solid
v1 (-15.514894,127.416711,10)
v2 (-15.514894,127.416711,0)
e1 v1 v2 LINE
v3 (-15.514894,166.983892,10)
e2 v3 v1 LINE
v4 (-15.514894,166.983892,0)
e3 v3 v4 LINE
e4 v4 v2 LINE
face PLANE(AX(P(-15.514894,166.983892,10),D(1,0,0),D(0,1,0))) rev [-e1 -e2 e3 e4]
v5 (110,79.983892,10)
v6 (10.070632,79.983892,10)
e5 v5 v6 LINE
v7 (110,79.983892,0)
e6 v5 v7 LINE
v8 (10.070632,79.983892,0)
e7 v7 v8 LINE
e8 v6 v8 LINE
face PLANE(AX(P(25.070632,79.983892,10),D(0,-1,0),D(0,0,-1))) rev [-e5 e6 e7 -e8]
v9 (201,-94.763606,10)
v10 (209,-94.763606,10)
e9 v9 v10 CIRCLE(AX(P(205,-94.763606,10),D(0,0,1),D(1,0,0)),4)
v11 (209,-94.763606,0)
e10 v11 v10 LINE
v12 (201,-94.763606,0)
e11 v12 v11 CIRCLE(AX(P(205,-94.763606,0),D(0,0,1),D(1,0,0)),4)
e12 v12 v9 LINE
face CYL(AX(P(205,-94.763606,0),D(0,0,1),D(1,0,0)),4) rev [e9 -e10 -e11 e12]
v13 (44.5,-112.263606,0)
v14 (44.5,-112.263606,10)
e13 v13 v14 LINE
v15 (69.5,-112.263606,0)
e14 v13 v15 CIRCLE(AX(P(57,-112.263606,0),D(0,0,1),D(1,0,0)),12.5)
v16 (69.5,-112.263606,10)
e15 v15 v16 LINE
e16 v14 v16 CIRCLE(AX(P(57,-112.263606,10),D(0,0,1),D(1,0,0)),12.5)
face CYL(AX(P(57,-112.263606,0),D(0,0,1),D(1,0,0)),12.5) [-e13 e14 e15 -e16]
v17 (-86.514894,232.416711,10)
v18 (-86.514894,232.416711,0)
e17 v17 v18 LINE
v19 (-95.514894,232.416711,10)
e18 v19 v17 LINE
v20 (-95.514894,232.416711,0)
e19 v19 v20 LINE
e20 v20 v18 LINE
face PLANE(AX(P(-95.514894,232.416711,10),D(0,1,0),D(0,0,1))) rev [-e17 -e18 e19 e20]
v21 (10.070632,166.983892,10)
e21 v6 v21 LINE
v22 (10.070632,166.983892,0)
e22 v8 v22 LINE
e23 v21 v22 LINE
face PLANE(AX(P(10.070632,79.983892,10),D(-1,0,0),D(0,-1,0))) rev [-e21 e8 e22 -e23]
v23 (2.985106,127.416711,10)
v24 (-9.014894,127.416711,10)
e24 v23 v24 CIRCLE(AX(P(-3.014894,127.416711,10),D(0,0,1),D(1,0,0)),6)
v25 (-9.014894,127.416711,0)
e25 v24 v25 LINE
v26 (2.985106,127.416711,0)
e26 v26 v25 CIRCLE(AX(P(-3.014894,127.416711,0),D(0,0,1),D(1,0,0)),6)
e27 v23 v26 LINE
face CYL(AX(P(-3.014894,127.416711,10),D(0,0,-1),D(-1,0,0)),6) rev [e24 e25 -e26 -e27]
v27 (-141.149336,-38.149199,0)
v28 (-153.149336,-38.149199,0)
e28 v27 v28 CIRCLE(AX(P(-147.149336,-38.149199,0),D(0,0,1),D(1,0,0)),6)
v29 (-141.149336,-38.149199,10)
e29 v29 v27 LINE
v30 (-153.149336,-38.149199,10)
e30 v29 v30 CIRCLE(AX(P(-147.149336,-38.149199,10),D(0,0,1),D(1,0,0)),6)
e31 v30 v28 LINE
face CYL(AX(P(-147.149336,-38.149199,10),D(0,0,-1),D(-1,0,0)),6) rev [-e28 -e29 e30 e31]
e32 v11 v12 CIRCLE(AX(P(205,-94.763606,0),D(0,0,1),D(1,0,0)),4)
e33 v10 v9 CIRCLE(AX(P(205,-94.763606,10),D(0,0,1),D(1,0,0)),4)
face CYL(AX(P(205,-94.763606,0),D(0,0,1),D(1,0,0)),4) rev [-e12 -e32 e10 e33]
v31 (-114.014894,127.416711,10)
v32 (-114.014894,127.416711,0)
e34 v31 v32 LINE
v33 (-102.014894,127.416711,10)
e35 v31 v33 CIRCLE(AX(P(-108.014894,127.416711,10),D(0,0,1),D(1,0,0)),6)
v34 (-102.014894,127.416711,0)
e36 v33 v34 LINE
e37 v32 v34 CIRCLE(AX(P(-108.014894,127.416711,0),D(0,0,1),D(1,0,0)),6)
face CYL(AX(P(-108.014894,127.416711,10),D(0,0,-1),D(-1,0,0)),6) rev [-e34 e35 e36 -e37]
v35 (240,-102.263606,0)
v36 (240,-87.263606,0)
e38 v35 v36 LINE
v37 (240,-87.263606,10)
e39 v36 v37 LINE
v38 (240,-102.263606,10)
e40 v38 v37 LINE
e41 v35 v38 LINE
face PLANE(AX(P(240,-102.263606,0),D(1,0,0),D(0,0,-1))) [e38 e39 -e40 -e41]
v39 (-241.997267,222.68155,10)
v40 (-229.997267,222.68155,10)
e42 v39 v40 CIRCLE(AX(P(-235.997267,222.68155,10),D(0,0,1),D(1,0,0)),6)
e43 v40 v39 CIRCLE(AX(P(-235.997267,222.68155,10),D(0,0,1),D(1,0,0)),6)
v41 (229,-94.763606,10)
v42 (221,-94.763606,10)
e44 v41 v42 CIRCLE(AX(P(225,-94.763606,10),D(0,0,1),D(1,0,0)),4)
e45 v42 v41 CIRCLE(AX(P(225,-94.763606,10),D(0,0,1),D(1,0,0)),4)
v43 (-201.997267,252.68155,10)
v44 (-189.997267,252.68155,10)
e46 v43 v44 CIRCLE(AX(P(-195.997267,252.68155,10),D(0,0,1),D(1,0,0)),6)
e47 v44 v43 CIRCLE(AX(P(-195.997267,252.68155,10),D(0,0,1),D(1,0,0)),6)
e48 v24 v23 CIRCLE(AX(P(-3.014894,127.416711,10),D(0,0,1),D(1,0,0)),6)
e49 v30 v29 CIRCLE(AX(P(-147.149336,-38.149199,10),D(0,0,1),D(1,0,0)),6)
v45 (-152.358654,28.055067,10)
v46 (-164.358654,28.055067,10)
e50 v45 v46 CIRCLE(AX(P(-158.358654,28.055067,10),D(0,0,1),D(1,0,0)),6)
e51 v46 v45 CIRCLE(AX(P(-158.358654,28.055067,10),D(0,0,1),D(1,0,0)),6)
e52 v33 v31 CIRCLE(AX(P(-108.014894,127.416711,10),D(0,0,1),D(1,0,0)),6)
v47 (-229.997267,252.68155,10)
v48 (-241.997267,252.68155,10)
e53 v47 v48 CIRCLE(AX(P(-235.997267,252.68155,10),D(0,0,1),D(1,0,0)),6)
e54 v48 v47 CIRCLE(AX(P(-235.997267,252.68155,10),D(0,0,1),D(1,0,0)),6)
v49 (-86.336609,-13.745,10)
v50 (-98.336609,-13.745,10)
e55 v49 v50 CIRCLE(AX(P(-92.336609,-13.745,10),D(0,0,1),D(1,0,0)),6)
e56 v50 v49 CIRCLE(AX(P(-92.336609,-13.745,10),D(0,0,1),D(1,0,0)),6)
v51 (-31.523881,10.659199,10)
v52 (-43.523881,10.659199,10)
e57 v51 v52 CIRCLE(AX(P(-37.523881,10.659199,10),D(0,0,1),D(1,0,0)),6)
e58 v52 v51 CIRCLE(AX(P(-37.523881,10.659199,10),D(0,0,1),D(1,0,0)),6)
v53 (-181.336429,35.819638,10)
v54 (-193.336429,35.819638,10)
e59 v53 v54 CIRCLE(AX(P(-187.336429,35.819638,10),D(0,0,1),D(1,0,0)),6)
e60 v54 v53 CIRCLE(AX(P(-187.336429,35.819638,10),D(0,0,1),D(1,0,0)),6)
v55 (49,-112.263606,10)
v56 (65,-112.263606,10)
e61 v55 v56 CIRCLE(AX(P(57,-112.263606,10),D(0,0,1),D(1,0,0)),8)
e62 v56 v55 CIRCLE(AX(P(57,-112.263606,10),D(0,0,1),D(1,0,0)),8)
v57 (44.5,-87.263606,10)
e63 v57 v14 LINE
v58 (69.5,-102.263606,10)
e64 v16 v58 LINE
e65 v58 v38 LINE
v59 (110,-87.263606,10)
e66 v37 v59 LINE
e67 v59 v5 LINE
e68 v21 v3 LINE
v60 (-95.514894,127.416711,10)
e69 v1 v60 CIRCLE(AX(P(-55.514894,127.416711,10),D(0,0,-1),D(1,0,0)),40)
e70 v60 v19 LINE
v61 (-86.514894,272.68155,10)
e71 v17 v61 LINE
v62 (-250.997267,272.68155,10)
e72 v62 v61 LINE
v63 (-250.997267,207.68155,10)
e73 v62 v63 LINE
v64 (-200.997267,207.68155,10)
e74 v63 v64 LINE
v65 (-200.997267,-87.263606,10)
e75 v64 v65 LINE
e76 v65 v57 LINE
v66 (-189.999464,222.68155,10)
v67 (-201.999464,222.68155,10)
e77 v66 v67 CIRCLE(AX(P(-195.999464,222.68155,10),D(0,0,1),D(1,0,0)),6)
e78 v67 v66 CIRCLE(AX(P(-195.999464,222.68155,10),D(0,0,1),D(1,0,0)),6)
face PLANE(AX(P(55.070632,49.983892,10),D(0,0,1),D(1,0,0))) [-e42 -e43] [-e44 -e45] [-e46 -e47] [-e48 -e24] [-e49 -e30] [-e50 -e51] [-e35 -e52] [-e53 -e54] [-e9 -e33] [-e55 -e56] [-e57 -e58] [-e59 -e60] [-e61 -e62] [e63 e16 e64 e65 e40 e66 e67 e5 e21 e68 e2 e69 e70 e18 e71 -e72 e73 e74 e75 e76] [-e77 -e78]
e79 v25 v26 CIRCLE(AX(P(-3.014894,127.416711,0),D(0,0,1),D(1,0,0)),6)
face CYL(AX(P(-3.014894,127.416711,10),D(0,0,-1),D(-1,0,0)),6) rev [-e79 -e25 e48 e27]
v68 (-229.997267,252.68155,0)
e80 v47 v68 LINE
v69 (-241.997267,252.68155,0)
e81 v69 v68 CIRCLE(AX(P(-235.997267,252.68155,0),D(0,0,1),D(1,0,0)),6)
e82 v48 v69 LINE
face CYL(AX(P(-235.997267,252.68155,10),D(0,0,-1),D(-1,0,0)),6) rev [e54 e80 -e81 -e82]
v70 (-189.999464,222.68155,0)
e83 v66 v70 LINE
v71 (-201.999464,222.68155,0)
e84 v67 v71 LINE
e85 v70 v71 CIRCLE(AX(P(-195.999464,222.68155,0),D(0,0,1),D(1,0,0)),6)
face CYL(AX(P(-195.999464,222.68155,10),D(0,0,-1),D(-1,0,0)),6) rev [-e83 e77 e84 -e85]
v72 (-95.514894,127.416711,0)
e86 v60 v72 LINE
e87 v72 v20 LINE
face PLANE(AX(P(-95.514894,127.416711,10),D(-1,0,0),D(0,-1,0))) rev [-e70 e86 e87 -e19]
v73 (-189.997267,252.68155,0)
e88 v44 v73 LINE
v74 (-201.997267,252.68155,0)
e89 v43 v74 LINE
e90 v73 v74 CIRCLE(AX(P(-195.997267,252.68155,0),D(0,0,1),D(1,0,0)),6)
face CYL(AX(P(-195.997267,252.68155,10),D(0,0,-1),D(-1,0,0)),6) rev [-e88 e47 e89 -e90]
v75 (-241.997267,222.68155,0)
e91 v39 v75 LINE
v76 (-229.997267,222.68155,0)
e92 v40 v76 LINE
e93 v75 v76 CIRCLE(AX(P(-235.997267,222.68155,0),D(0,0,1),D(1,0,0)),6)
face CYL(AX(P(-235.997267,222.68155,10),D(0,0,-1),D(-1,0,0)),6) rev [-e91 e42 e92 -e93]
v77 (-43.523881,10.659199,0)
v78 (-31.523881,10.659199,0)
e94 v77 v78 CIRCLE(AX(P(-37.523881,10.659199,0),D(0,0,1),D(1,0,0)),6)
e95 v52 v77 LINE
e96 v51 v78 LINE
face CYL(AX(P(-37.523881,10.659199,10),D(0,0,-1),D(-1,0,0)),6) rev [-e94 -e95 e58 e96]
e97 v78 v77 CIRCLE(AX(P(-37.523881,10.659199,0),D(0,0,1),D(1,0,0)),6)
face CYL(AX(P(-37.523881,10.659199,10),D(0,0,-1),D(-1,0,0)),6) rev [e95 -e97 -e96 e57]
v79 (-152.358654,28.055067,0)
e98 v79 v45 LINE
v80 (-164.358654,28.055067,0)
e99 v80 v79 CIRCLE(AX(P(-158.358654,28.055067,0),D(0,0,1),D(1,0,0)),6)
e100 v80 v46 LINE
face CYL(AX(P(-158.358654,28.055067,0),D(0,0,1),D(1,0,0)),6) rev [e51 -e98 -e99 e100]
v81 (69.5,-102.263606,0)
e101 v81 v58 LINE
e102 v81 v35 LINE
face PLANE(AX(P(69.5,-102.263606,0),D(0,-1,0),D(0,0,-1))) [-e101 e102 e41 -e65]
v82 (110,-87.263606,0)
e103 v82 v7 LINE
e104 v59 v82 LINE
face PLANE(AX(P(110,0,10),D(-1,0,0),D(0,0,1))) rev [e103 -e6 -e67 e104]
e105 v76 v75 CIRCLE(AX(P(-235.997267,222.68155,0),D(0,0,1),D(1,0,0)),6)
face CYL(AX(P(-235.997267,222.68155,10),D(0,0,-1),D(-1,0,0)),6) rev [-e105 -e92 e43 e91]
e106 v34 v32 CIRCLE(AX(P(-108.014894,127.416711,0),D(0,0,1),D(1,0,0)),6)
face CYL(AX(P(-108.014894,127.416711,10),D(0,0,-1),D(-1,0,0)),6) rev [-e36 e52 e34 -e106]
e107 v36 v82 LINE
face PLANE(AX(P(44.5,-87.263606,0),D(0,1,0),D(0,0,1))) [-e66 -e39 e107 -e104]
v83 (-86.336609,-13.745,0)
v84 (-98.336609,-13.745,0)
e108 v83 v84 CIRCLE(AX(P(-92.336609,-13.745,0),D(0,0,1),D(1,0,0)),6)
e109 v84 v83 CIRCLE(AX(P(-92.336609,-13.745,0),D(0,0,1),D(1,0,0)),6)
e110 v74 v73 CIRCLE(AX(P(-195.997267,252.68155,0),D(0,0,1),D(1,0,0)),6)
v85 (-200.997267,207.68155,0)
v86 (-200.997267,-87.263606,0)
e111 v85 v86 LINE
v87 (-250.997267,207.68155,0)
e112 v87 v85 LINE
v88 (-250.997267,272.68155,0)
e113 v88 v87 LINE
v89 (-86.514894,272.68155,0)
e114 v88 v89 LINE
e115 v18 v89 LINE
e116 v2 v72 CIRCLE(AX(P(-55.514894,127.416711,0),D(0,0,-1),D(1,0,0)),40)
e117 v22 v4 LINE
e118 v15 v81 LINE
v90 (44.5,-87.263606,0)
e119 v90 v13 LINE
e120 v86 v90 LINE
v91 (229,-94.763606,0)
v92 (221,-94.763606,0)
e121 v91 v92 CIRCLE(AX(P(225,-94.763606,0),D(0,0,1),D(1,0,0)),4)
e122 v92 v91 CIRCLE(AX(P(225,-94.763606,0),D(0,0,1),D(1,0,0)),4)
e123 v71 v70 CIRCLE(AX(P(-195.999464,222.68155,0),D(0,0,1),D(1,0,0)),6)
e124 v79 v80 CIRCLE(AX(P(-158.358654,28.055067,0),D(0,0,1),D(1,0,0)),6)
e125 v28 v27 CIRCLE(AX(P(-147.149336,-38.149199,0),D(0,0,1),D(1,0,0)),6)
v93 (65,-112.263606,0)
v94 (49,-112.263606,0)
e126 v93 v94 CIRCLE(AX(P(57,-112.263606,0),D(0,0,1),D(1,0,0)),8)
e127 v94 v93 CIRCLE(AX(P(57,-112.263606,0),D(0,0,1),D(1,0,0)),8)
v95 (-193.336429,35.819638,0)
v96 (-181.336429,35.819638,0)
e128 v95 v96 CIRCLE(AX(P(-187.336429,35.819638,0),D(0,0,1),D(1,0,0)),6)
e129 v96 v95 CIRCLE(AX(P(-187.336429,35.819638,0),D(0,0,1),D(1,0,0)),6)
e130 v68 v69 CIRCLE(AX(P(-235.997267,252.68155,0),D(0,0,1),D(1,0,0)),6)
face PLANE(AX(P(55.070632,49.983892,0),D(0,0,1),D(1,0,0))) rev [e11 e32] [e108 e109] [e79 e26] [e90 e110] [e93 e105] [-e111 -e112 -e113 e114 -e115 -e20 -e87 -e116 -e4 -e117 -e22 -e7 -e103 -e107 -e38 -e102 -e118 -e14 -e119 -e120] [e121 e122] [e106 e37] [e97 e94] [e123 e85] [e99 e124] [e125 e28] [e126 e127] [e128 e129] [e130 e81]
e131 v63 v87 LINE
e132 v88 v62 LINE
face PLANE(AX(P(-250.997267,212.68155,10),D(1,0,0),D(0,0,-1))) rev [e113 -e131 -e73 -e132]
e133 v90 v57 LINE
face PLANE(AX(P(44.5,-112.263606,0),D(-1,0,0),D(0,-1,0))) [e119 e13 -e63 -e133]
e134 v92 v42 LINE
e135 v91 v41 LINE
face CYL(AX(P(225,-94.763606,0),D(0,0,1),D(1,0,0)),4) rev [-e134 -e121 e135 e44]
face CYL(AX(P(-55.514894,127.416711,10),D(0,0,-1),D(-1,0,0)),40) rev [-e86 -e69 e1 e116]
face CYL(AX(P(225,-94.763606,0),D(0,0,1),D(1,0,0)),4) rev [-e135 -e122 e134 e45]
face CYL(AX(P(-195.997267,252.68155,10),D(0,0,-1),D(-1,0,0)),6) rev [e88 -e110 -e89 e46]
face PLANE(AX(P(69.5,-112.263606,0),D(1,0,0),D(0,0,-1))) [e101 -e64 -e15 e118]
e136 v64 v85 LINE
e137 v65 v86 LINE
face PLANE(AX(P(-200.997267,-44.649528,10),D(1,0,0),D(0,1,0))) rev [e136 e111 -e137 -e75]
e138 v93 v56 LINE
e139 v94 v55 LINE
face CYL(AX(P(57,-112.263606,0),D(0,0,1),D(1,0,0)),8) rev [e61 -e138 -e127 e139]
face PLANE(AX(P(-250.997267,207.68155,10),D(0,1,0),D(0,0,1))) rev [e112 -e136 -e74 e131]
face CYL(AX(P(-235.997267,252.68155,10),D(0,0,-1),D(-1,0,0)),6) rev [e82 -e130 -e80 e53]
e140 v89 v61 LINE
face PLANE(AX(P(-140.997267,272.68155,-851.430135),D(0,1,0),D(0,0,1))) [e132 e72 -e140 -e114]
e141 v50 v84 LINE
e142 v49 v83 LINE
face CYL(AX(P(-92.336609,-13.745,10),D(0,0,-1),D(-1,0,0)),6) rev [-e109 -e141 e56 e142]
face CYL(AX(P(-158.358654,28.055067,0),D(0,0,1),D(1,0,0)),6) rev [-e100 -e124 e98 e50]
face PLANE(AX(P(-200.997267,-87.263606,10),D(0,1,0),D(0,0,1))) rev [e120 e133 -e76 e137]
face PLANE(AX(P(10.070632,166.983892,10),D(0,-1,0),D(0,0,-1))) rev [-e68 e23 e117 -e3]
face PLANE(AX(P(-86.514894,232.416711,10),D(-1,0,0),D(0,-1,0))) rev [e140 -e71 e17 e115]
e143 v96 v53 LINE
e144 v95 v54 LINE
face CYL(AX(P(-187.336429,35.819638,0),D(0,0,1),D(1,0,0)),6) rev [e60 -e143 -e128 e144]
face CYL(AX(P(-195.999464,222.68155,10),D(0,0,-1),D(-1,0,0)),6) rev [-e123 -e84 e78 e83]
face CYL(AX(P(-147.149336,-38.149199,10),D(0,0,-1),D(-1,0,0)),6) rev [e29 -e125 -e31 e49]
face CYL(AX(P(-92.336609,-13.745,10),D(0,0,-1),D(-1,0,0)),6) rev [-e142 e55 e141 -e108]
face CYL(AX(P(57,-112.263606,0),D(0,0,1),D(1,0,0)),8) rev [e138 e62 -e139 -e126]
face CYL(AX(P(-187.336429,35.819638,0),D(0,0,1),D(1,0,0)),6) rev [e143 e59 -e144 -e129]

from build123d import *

# Parameters (mm, degrees)
SKETCH_1_R               = 5
SKETCH_1_R_2             = 6
EXTRUDE_1_DEPTH          = 10
SKETCH_2_R               = 6
CUT_EXTRUDE_1_DEPTH      = 10
SKETCH_3_R               = 8
SKETCH_3_R_2             = 4
EXTRUDE_2_DEPTH          = 10
CUT_EXTRUDE_3_DEPTH      = 417.865256367
CUT_EXTRUDE_3_DEPTH_BACK = 10
SKETCH_4_R               = 5
SKETCH_5_R               = 5
EXTRUDE_3_DEPTH          = 10
SKETCH_6_R               = 5
EXTRUDE_4_DEPTH          = 10
EXTRUDE_5_DEPTH          = 10


with BuildPart() as part:
    # 草图1 → 凸台-拉伸1 (new body)
    with BuildSketch(Plane.XY):
        with BuildLine():
            Line((-200.997267146, -87.263605576), (110, -87.263605576))
            Line((110, -87.263605576), (110, 0))
            Line((110, 0), (110, 79.983892276))
            Line((110, 79.983892276), (85.070632456, 79.983892276))
            Line((85.070632456, 79.983892276), (85.070632456, 49.983892276))
            ThreePointArc((85.070632456, 49.983892276), (55.070632456, 19.983892276), (25.070632456, 49.983892276))
            Line((25.070632456, 49.983892276), (25.070632456, 79.983892276))
            Line((25.070632456, 79.983892276), (10.070632456, 79.983892276))
            Line((10.070632456, 79.983892276), (10.070632456, 166.983892276))
            Line((10.070632456, 166.983892276), (-15.514893523, 166.983892276))
            Line((-15.514893523, 166.983892276), (-15.514893523, 127.416711183))
            ThreePointArc((-15.514893523, 127.416711183), (-55.514893523, 87.416711183), (-95.514893523, 127.416711183))
            Line((-95.514893523, 127.416711183), (-95.514893523, 232.416711183))
            Line((-95.514893523, 232.416711183), (-86.514893523, 232.416711183))
            Line((-86.514893523, 232.416711183), (-86.514893523, 332.416711183))
            Line((-86.514893523, 332.416711183), (-110.997267146, 332.416711183))
            Line((-110.997267146, 332.416711183), (-110.997267146, 302.681550212))
            ThreePointArc((-110.997267146, 302.681550212), (-140.997267146, 272.681550212), (-170.997267146, 302.681550212))
            Line((-170.997267146, 302.681550212), (-170.997267146, 332.681550212))
            Line((-170.997267146, 332.681550212), (-200.997267146, 332.681550212))
            Line((-200.997267146, 332.681550212), (-250.997267146, 332.681550212))
            Line((-250.997267146, 332.681550212), (-250.997267146, 212.681550212))
            Line((-250.997267146, 212.681550212), (-250.997267146, 207.681550212))
            Line((-250.997267146, 207.681550212), (-200.997267146, 207.681550212))
            Line((-200.997267146, 207.681550212), (-200.997267146, 182.681550212))
            Line((-200.997267146, 182.681550212), (-200.997267146, -44.649528276))
            Line((-200.997267146, -44.649528276), (-200.997267146, -87.263605576))
        make_face()
        with Locations((96.070632456, 49.983892276)):
            Circle(SKETCH_1_R, mode=Mode.SUBTRACT)
        with Locations((14.070632456, 49.983892276)):
            Circle(SKETCH_1_R, mode=Mode.SUBTRACT)
        with Locations((-3.014893523, 127.416711183)):
            Circle(SKETCH_1_R_2, mode=Mode.SUBTRACT)
        with Locations((-108.014893523, 127.416711183)):
            Circle(SKETCH_1_R_2, mode=Mode.SUBTRACT)
        with Locations((-99.997267146, 302.681550212)):
            Circle(SKETCH_1_R, mode=Mode.SUBTRACT)
        with Locations((-181.997266842, 302.67655009)):
            Circle(SKETCH_1_R, mode=Mode.SUBTRACT)
        with Locations((-37.523881476, 10.659198545)):
            Circle(SKETCH_1_R_2, mode=Mode.SUBTRACT)
        with Locations((-92.336608934, -13.745000039)):
            Circle(SKETCH_1_R_2, mode=Mode.SUBTRACT)
        with Locations((-147.149336393, -38.149198624)):
            Circle(SKETCH_1_R_2, mode=Mode.SUBTRACT)
        with Locations((-235.997267146, 222.681550212)):
            Circle(SKETCH_1_R_2, mode=Mode.SUBTRACT)
        with Locations((-195.999464127, 222.681550212)):
            Circle(SKETCH_1_R_2, mode=Mode.SUBTRACT)
        with Locations((-235.997267146, 252.681550212)):
            Circle(SKETCH_1_R_2, mode=Mode.SUBTRACT)
        with Locations((-195.997267146, 252.681550131)):
            Circle(SKETCH_1_R_2, mode=Mode.SUBTRACT)
    extrude(amount=EXTRUDE_1_DEPTH)

    # 草图2 → 切除-拉伸1 (cut)
    with BuildSketch(Plane.XY.offset(10)):
        with Locations((-158.358654267, 28.055066971)):
            Circle(SKETCH_2_R)
        with Locations((-187.336429056, 35.819638324)):
            Circle(SKETCH_2_R)
    extrude(amount=-CUT_EXTRUDE_1_DEPTH, mode=Mode.SUBTRACT)

    # 草图3 → 凸台-拉伸2 (add)
    with BuildSketch(Plane.XY.offset(10)):
        with BuildLine():
            Line((110, -87.263605576), (62, -87.263605576))
            Line((62, -87.263605576), (44.5, -87.263605576))
            Line((44.5, -87.263605576), (44.5, -112.263605576))
            ThreePointArc((44.5, -112.263605576), (57, -124.763605576), (69.5, -112.263605576))
            Line((69.5, -112.263605576), (69.5, -102.263605576))
            Line((69.5, -102.263605576), (240, -102.263605576))
            Line((240, -102.263605576), (240, -87.263605576))
            Line((240, -87.263605576), (110, -87.263605576))
        make_face()
        with Locations((57, -112.263605576)):
            Circle(SKETCH_3_R, mode=Mode.SUBTRACT)
        with Locations((225, -94.763605576)):
            Circle(SKETCH_3_R_2, mode=Mode.SUBTRACT)
        with Locations((205, -94.763605576)):
            Circle(SKETCH_3_R_2, mode=Mode.SUBTRACT)
    extrude(amount=-EXTRUDE_2_DEPTH)

    # 草图4 → 切除-拉伸3 (cut, two sides: drawn at the far end of the back side and taken through both)
    # profile 1 of 2: a face of its own
    with BuildSketch(Plane(origin=(0, 0, 0), x_dir=(-1, 0, 0), z_dir=(0, 0, -1)).offset(-CUT_EXTRUDE_3_DEPTH_BACK)):
        with BuildLine():
            ThreePointArc((170.997267146, 302.681550212), (162.210470582, 281.468346776), (140.997267146, 272.681550212))
            Line((140.997267146, 272.681550212), (250.997267146, 272.681550212))
            Line((250.997267146, 272.681550212), (250.997267146, 332.681550212))
            Line((250.997267146, 332.681550212), (170.997267146, 332.681550212))
            Line((170.997267146, 332.681550212), (170.997267146, 302.681550212))
        make_face()
        with Locations((181.997266842, 302.67655009)):
            Circle(SKETCH_4_R, mode=Mode.SUBTRACT)
    # profile 2 of 2: a face of its own
    with BuildSketch(Plane(origin=(0, 0, 0), x_dir=(-1, 0, 0), z_dir=(0, 0, -1)).offset(-CUT_EXTRUDE_3_DEPTH_BACK)):
        with BuildLine():
            Line((86.514893523, 272.681550212), (140.997267146, 272.681550212))
            ThreePointArc((140.997267146, 272.681550212), (119.784063711, 281.468346776), (110.997267146, 302.681550212))
            Line((110.997267146, 302.681550212), (110.997267146, 332.416711183))
            Line((110.997267146, 332.416711183), (86.514893523, 332.416711183))
            Line((86.514893523, 332.416711183), (86.514893523, 272.681550212))
        make_face()
        with Locations((99.997267146, 302.681550212)):
            Circle(SKETCH_4_R, mode=Mode.SUBTRACT)
    extrude(amount=CUT_EXTRUDE_3_DEPTH + CUT_EXTRUDE_3_DEPTH_BACK, mode=Mode.SUBTRACT)

    # 草图5 → 凸台-拉伸3 (add)
    with BuildSketch(Plane(origin=(0, 0, 0), x_dir=(-1, 0, 0), z_dir=(0, 0, -1))):
        with Locations((-96.070632456, 49.983892276)):
            Circle(SKETCH_5_R)
    extrude(amount=-EXTRUDE_3_DEPTH)

    # 草图6 → 凸台-拉伸4 (add)
    with BuildSketch(Plane(origin=(0, 0, 0), x_dir=(-1, 0, 0), z_dir=(0, 0, -1))):
        with Locations((-14.070632456, 49.983892276)):
            Circle(SKETCH_6_R)
    extrude(amount=-EXTRUDE_4_DEPTH)

    # 草图7 → 凸台-拉伸5 (add)
    with BuildSketch(Plane(origin=(0, 0, 0), x_dir=(-1, 0, 0), z_dir=(0, 0, -1))):
        with BuildLine():
            Line((-85.070632456, 79.983892276), (-85.070632456, 49.983892276))
            ThreePointArc((-85.070632456, 49.983892276), (-55.070632456, 19.983892276), (-25.070632456, 49.983892276))
            Line((-25.070632456, 49.983892276), (-25.070632456, 79.983892276))
            Line((-25.070632456, 79.983892276), (-85.070632456, 79.983892276))
        make_face()
    extrude(amount=-EXTRUDE_5_DEPTH)


solid = part.part
